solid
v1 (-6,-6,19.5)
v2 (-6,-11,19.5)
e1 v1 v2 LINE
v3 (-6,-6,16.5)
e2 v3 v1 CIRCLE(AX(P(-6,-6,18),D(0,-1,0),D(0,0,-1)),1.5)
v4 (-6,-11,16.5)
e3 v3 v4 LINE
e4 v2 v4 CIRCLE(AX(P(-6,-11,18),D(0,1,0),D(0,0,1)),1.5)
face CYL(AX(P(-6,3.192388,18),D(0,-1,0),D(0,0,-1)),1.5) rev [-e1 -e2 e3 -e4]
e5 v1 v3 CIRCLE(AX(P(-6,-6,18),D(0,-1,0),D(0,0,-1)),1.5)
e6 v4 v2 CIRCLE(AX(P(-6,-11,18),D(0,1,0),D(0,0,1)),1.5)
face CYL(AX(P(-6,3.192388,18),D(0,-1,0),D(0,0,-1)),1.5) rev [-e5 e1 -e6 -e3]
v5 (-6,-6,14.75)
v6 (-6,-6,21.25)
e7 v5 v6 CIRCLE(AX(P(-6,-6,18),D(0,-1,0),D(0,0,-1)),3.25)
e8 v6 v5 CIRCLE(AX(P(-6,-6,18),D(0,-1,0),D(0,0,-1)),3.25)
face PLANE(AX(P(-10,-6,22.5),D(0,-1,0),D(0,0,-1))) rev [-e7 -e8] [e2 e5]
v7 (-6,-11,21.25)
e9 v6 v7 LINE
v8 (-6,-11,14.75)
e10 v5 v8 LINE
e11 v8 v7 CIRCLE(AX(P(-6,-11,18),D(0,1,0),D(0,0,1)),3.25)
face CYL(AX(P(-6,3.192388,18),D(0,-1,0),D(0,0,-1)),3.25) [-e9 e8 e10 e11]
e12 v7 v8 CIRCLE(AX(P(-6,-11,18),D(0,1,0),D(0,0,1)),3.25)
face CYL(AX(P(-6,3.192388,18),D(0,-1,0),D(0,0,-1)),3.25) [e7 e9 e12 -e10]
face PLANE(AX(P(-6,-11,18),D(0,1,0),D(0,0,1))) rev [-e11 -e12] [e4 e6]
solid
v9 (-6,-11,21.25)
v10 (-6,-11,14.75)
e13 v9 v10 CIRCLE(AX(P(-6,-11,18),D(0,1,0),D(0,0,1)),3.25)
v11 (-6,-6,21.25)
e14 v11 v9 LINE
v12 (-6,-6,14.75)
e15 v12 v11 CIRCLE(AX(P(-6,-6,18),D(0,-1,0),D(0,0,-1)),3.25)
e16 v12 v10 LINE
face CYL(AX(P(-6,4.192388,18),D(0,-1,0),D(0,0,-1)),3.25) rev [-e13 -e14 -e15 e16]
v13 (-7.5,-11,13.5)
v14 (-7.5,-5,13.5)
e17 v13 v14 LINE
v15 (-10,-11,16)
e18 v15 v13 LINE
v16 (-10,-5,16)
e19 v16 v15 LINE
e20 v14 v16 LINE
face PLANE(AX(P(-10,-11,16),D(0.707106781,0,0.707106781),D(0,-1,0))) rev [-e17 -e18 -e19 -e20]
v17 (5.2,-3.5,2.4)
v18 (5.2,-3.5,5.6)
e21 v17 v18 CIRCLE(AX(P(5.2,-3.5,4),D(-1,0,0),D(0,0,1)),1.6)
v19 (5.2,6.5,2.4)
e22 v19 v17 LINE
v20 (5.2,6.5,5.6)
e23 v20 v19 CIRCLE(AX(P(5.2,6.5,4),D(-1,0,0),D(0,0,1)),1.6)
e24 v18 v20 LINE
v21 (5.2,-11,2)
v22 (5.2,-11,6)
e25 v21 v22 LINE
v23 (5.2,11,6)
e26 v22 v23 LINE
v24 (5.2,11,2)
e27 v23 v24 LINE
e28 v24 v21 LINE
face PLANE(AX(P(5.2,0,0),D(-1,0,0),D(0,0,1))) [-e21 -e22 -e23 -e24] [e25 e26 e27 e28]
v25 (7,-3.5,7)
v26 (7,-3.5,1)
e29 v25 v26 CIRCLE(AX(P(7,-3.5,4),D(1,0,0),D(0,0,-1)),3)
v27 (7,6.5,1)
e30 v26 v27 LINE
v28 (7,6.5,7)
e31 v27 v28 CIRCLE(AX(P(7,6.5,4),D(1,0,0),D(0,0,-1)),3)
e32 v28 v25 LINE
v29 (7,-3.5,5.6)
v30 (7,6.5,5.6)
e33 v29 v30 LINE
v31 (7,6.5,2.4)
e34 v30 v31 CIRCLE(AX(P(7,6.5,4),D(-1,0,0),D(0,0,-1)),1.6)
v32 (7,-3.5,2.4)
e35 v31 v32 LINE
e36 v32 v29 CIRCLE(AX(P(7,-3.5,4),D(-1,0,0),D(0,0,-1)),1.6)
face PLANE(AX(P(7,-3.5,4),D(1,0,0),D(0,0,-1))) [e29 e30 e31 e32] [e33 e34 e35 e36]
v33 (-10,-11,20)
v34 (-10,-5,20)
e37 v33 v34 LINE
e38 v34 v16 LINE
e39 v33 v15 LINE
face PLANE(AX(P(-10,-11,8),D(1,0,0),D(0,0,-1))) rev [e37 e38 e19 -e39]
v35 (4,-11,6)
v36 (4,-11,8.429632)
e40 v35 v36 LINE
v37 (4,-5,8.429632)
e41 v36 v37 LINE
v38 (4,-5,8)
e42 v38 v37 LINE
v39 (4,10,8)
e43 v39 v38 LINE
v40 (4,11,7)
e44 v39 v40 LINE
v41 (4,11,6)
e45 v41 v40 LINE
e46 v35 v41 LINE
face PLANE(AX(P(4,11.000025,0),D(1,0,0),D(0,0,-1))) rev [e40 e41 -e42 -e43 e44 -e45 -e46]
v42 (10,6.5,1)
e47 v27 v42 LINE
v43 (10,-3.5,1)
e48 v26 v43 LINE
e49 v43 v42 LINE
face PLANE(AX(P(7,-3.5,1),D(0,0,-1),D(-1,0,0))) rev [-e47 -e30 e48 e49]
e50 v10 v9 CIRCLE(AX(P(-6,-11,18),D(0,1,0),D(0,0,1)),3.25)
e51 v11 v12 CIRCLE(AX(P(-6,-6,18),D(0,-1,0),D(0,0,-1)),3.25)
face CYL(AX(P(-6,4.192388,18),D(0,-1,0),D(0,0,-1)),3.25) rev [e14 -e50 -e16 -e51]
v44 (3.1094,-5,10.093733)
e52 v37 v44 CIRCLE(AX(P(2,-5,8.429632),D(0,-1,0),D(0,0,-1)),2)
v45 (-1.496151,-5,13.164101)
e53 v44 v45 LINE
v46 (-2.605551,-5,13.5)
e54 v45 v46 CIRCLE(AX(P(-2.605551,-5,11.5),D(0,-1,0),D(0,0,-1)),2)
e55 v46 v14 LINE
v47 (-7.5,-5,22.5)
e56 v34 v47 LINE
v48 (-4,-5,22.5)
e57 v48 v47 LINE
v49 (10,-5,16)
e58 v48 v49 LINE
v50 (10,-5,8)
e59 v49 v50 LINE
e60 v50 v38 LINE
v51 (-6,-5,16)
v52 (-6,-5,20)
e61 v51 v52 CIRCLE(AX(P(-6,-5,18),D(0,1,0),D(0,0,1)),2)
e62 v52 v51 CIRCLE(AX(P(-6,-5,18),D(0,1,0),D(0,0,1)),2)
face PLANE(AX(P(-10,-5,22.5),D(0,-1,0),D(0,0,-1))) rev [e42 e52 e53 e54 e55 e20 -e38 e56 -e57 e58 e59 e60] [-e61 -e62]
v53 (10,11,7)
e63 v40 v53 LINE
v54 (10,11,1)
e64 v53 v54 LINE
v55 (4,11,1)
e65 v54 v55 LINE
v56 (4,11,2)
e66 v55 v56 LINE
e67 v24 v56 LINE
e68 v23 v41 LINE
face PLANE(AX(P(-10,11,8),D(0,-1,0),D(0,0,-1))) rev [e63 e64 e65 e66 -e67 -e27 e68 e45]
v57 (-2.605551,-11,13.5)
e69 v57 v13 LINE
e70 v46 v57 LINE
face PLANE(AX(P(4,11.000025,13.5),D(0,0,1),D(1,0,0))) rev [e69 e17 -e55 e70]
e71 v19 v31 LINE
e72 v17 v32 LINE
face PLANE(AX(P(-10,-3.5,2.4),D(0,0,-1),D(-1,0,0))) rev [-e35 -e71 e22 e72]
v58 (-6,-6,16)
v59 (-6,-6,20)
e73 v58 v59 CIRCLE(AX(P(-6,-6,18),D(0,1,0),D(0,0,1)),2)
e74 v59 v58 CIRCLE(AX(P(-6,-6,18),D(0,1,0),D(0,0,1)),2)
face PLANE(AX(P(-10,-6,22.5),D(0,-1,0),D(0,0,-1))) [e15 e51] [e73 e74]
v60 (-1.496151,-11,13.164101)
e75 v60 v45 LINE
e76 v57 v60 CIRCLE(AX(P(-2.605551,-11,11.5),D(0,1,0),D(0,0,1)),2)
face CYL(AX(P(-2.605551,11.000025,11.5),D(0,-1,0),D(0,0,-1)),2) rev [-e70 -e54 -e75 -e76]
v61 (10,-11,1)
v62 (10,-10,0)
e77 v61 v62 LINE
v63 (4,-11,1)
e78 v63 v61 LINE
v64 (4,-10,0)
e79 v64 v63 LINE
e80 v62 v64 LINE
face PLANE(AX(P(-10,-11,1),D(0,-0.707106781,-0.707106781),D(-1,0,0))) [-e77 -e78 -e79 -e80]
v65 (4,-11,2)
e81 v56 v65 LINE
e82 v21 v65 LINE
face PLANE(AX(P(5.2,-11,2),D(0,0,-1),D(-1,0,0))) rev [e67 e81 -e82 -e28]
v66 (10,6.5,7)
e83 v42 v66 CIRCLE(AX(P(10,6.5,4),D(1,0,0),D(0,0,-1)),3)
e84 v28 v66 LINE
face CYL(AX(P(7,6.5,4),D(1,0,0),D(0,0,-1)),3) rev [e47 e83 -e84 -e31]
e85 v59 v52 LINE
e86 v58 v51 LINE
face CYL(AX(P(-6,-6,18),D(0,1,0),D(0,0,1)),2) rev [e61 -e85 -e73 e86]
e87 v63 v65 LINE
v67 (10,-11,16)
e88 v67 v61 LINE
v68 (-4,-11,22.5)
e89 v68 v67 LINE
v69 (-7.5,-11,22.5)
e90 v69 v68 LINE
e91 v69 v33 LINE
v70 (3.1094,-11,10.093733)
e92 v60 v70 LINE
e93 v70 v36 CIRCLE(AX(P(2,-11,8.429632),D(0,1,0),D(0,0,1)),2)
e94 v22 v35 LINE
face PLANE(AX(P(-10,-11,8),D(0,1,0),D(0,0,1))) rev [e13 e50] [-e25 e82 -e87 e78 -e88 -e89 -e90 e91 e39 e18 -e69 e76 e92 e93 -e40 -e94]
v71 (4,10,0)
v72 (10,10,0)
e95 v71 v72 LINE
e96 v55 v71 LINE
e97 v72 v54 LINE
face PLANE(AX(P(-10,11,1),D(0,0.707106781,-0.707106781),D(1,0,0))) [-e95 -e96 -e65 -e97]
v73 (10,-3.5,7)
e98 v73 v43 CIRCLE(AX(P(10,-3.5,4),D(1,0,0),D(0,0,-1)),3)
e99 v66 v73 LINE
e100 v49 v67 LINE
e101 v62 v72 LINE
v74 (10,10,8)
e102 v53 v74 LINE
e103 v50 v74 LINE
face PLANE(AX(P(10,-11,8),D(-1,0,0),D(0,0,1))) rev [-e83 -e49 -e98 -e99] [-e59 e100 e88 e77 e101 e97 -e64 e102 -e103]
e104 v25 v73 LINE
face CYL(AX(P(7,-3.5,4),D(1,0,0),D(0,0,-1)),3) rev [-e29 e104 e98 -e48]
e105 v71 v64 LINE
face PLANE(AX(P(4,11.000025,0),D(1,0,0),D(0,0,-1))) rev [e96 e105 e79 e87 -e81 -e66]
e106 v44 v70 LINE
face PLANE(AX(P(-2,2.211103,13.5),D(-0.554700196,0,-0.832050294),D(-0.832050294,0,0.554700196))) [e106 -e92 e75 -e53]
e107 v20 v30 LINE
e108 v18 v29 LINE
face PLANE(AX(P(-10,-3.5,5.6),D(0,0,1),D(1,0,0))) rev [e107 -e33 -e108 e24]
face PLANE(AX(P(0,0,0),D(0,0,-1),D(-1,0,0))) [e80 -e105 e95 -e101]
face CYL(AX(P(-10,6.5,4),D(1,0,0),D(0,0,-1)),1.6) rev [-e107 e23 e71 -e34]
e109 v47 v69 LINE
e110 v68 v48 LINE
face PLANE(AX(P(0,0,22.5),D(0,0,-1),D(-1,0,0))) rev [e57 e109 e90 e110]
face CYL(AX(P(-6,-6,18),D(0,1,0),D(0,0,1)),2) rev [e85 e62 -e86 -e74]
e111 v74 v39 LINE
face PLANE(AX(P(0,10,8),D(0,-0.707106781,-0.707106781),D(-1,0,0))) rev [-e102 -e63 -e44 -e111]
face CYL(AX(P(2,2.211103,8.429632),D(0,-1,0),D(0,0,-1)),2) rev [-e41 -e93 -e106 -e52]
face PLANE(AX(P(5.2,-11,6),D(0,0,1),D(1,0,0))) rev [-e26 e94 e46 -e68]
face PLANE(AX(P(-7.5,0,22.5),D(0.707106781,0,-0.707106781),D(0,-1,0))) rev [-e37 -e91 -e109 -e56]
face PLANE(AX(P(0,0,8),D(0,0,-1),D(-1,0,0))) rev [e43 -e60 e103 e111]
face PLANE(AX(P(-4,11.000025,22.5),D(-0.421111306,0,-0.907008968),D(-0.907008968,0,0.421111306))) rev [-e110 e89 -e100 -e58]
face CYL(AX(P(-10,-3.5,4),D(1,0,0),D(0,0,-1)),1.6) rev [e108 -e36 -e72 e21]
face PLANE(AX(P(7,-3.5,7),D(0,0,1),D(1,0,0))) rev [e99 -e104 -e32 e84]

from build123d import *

# Parameters (mm, degrees)
SKETCH1_W           = 20
SKETCH1_H           = 22
BOSS_EXTRUDE1_DEPTH = 8
SKETCH2_W           = 20
SKETCH2_H           = 6
BOSS_EXTRUDE2_DEPTH = 14.5
SKETCH4_R           = 3.25
CUT_EXTRUDE2_DEPTH  = 5
SKETCH5_R           = 3.25
SKETCH5_R_2         = 1.5
BOSS_EXTRUDE3_DEPTH = 5
SKETCH6_W           = 14
SKETCH6_H           = 13.5
CUT_EXTRUDE3_DEPTH  = 34.018933962
SKETCH7_W           = 4
SKETCH7_H           = 22
CUT_EXTRUDE4_DEPTH  = 1.2
CUT_EXTRUDE5_DEPTH  = 34.018933962
CUT_EXTRUDE6_DEPTH  = 33.050741021
CUT_EXTRUDE7_DEPTH  = 3
CHAMFER3_SIZE       = 2.5
CHAMFER4_SIZE       = 1
BOSS_EXTRUDE4_DEPTH = 6
FILLET2_R           = 2
SKETCH14_R          = 1.5
CUT_EXTRUDE8_DEPTH  = 34.018933962
SKETCH15_R          = 2
CUT_EXTRUDE9_DEPTH  = 1


with BuildPart() as part:
    # Sketch1 → Boss-Extrude1 (new body)
    with BuildSketch(Plane.XY):
        Rectangle(SKETCH1_W, SKETCH1_H)
    extrude(amount=BOSS_EXTRUDE1_DEPTH)

    # Sketch2 → Boss-Extrude2 (add)
    with BuildSketch(Plane.XY.offset(8)):
        with Locations((0, -8)):
            Rectangle(SKETCH2_W, SKETCH2_H)
    extrude(amount=BOSS_EXTRUDE2_DEPTH)

    # Sketch4 → Cut-Extrude2 (cut)
    with BuildSketch(Plane(origin=(0, -11, 0), x_dir=(1, 0, 0), z_dir=(0, 1, 0))):
        with Locations(Location((-6, -18, 0), (0, 0, 90))):
            Circle(SKETCH4_R)
    extrude(amount=CUT_EXTRUDE2_DEPTH, mode=Mode.SUBTRACT)

    # Sketch6 → Cut-Extrude3 (cut, through all)
    with BuildSketch(Plane.XZ.offset(11)):
        with Locations((-3, 6.75)):
            Rectangle(SKETCH6_W, SKETCH6_H)
    extrude(amount=-CUT_EXTRUDE3_DEPTH, mode=Mode.SUBTRACT)

    # Sketch7 → Cut-Extrude4 (cut)
    with BuildSketch(Plane.ZY.offset(-4)):
        with Locations((4, 0)):
            Rectangle(SKETCH7_W, SKETCH7_H)
    extrude(amount=-CUT_EXTRUDE4_DEPTH, mode=Mode.SUBTRACT)

    # Sketch8 → Cut-Extrude5 (cut, through all)
    with BuildSketch(Plane.XZ.offset(11)):
        Polygon((-4, 22.5), (10, 16), (10, 22.5), align=None)
    extrude(amount=-CUT_EXTRUDE5_DEPTH, mode=Mode.SUBTRACT)

    # Sketch11 → Cut-Extrude6 (cut, through all)
    with BuildSketch(Plane(origin=(10, 0, 0), x_dir=(0, 0, -1), z_dir=(1, 0, 0))):
        with BuildLine():
            Line((-5.6, -3.5), (-5.6, 6.5))
            ThreePointArc((-5.6, 6.5), (-4, 8.1), (-2.4, 6.5))
            Line((-2.4, 6.5), (-2.4, -3.5))
            ThreePointArc((-2.4, -3.5), (-4, -5.1), (-5.6, -3.5))
        make_face()
    extrude(amount=-CUT_EXTRUDE6_DEPTH, mode=Mode.SUBTRACT)

    # Sketch12 → Cut-Extrude7 (cut)
    with BuildSketch(Plane(origin=(10, 0, 0), x_dir=(0, 0, -1), z_dir=(1, 0, 0))):
        with BuildLine():
            Line((-7, -3.5), (-7, 6.5))
            ThreePointArc((-7, 6.5), (-4, 9.5), (-1, 6.5))
            Line((-1, 6.5), (-1, -3.5))
            ThreePointArc((-1, -3.5), (-4, -6.5), (-7, -3.5))
        make_face()
    extrude(amount=-CUT_EXTRUDE7_DEPTH, mode=Mode.SUBTRACT)

    # Chamfer3
    chamfer3_edges = [part.edges().sort_by_distance(p)[0] for p in [
        (-10, -8, 22.5),
        (-10, -8, 13.5),
    ]]
    chamfer(chamfer3_edges, length=CHAMFER3_SIZE)

    # Chamfer4
    chamfer4_edges = [part.edges().sort_by_distance(p)[0] for p in [
        (7, -11, 0),
        (7, 11, 0),
        (7, 11, 8),
    ]]
    chamfer(chamfer4_edges, length=CHAMFER4_SIZE)

    # Sketch13 → Boss-Extrude4 (add)
    with BuildSketch(Plane.XZ.offset(11)):
        Polygon((-2, 13.5), (4, 9.5), (4, 13.5), align=None)
    extrude(amount=-BOSS_EXTRUDE4_DEPTH)

    # Fillet2
    fillet2_edges = [part.edges().sort_by_distance(p)[0] for p in [
        (-2, -8, 13.5),
        (4, -8, 9.5),
    ]]
    fillet(fillet2_edges, radius=FILLET2_R)

    # Sketch14 → Cut-Extrude8 (cut, through all)
    with BuildSketch(Plane.XZ.offset(11)):
        with Locations(Location((-6, 18, 0), (0, 0, 270))):
            Circle(SKETCH14_R)
    extrude(amount=-CUT_EXTRUDE8_DEPTH, mode=Mode.SUBTRACT)

    # Sketch15 → Cut-Extrude9 (cut)
    with BuildSketch(Plane(origin=(0, -5, 0), x_dir=(1, 0, 0), z_dir=(0, 1, 0))):
        with Locations(Location((-6, -18, 0), (0, 0, 270))):
            Circle(SKETCH15_R)
    extrude(amount=-CUT_EXTRUDE9_DEPTH, mode=Mode.SUBTRACT)


with BuildPart() as body_2:
    # Sketch5 → Boss-Extrude3 (new body)
    with BuildSketch(Plane(origin=(0, -11, 0), x_dir=(1, 0, 0), z_dir=(0, 1, 0))):
        with Locations(Location((-6, -18, 0), (0, 0, 90))):
            Circle(SKETCH5_R)
        with Locations(Location((-6, -18, 0), (0, 0, 90))):
            Circle(SKETCH5_R_2, mode=Mode.SUBTRACT)
    extrude(amount=BOSS_EXTRUDE3_DEPTH)


solid = Compound([part.part, body_2.part])
